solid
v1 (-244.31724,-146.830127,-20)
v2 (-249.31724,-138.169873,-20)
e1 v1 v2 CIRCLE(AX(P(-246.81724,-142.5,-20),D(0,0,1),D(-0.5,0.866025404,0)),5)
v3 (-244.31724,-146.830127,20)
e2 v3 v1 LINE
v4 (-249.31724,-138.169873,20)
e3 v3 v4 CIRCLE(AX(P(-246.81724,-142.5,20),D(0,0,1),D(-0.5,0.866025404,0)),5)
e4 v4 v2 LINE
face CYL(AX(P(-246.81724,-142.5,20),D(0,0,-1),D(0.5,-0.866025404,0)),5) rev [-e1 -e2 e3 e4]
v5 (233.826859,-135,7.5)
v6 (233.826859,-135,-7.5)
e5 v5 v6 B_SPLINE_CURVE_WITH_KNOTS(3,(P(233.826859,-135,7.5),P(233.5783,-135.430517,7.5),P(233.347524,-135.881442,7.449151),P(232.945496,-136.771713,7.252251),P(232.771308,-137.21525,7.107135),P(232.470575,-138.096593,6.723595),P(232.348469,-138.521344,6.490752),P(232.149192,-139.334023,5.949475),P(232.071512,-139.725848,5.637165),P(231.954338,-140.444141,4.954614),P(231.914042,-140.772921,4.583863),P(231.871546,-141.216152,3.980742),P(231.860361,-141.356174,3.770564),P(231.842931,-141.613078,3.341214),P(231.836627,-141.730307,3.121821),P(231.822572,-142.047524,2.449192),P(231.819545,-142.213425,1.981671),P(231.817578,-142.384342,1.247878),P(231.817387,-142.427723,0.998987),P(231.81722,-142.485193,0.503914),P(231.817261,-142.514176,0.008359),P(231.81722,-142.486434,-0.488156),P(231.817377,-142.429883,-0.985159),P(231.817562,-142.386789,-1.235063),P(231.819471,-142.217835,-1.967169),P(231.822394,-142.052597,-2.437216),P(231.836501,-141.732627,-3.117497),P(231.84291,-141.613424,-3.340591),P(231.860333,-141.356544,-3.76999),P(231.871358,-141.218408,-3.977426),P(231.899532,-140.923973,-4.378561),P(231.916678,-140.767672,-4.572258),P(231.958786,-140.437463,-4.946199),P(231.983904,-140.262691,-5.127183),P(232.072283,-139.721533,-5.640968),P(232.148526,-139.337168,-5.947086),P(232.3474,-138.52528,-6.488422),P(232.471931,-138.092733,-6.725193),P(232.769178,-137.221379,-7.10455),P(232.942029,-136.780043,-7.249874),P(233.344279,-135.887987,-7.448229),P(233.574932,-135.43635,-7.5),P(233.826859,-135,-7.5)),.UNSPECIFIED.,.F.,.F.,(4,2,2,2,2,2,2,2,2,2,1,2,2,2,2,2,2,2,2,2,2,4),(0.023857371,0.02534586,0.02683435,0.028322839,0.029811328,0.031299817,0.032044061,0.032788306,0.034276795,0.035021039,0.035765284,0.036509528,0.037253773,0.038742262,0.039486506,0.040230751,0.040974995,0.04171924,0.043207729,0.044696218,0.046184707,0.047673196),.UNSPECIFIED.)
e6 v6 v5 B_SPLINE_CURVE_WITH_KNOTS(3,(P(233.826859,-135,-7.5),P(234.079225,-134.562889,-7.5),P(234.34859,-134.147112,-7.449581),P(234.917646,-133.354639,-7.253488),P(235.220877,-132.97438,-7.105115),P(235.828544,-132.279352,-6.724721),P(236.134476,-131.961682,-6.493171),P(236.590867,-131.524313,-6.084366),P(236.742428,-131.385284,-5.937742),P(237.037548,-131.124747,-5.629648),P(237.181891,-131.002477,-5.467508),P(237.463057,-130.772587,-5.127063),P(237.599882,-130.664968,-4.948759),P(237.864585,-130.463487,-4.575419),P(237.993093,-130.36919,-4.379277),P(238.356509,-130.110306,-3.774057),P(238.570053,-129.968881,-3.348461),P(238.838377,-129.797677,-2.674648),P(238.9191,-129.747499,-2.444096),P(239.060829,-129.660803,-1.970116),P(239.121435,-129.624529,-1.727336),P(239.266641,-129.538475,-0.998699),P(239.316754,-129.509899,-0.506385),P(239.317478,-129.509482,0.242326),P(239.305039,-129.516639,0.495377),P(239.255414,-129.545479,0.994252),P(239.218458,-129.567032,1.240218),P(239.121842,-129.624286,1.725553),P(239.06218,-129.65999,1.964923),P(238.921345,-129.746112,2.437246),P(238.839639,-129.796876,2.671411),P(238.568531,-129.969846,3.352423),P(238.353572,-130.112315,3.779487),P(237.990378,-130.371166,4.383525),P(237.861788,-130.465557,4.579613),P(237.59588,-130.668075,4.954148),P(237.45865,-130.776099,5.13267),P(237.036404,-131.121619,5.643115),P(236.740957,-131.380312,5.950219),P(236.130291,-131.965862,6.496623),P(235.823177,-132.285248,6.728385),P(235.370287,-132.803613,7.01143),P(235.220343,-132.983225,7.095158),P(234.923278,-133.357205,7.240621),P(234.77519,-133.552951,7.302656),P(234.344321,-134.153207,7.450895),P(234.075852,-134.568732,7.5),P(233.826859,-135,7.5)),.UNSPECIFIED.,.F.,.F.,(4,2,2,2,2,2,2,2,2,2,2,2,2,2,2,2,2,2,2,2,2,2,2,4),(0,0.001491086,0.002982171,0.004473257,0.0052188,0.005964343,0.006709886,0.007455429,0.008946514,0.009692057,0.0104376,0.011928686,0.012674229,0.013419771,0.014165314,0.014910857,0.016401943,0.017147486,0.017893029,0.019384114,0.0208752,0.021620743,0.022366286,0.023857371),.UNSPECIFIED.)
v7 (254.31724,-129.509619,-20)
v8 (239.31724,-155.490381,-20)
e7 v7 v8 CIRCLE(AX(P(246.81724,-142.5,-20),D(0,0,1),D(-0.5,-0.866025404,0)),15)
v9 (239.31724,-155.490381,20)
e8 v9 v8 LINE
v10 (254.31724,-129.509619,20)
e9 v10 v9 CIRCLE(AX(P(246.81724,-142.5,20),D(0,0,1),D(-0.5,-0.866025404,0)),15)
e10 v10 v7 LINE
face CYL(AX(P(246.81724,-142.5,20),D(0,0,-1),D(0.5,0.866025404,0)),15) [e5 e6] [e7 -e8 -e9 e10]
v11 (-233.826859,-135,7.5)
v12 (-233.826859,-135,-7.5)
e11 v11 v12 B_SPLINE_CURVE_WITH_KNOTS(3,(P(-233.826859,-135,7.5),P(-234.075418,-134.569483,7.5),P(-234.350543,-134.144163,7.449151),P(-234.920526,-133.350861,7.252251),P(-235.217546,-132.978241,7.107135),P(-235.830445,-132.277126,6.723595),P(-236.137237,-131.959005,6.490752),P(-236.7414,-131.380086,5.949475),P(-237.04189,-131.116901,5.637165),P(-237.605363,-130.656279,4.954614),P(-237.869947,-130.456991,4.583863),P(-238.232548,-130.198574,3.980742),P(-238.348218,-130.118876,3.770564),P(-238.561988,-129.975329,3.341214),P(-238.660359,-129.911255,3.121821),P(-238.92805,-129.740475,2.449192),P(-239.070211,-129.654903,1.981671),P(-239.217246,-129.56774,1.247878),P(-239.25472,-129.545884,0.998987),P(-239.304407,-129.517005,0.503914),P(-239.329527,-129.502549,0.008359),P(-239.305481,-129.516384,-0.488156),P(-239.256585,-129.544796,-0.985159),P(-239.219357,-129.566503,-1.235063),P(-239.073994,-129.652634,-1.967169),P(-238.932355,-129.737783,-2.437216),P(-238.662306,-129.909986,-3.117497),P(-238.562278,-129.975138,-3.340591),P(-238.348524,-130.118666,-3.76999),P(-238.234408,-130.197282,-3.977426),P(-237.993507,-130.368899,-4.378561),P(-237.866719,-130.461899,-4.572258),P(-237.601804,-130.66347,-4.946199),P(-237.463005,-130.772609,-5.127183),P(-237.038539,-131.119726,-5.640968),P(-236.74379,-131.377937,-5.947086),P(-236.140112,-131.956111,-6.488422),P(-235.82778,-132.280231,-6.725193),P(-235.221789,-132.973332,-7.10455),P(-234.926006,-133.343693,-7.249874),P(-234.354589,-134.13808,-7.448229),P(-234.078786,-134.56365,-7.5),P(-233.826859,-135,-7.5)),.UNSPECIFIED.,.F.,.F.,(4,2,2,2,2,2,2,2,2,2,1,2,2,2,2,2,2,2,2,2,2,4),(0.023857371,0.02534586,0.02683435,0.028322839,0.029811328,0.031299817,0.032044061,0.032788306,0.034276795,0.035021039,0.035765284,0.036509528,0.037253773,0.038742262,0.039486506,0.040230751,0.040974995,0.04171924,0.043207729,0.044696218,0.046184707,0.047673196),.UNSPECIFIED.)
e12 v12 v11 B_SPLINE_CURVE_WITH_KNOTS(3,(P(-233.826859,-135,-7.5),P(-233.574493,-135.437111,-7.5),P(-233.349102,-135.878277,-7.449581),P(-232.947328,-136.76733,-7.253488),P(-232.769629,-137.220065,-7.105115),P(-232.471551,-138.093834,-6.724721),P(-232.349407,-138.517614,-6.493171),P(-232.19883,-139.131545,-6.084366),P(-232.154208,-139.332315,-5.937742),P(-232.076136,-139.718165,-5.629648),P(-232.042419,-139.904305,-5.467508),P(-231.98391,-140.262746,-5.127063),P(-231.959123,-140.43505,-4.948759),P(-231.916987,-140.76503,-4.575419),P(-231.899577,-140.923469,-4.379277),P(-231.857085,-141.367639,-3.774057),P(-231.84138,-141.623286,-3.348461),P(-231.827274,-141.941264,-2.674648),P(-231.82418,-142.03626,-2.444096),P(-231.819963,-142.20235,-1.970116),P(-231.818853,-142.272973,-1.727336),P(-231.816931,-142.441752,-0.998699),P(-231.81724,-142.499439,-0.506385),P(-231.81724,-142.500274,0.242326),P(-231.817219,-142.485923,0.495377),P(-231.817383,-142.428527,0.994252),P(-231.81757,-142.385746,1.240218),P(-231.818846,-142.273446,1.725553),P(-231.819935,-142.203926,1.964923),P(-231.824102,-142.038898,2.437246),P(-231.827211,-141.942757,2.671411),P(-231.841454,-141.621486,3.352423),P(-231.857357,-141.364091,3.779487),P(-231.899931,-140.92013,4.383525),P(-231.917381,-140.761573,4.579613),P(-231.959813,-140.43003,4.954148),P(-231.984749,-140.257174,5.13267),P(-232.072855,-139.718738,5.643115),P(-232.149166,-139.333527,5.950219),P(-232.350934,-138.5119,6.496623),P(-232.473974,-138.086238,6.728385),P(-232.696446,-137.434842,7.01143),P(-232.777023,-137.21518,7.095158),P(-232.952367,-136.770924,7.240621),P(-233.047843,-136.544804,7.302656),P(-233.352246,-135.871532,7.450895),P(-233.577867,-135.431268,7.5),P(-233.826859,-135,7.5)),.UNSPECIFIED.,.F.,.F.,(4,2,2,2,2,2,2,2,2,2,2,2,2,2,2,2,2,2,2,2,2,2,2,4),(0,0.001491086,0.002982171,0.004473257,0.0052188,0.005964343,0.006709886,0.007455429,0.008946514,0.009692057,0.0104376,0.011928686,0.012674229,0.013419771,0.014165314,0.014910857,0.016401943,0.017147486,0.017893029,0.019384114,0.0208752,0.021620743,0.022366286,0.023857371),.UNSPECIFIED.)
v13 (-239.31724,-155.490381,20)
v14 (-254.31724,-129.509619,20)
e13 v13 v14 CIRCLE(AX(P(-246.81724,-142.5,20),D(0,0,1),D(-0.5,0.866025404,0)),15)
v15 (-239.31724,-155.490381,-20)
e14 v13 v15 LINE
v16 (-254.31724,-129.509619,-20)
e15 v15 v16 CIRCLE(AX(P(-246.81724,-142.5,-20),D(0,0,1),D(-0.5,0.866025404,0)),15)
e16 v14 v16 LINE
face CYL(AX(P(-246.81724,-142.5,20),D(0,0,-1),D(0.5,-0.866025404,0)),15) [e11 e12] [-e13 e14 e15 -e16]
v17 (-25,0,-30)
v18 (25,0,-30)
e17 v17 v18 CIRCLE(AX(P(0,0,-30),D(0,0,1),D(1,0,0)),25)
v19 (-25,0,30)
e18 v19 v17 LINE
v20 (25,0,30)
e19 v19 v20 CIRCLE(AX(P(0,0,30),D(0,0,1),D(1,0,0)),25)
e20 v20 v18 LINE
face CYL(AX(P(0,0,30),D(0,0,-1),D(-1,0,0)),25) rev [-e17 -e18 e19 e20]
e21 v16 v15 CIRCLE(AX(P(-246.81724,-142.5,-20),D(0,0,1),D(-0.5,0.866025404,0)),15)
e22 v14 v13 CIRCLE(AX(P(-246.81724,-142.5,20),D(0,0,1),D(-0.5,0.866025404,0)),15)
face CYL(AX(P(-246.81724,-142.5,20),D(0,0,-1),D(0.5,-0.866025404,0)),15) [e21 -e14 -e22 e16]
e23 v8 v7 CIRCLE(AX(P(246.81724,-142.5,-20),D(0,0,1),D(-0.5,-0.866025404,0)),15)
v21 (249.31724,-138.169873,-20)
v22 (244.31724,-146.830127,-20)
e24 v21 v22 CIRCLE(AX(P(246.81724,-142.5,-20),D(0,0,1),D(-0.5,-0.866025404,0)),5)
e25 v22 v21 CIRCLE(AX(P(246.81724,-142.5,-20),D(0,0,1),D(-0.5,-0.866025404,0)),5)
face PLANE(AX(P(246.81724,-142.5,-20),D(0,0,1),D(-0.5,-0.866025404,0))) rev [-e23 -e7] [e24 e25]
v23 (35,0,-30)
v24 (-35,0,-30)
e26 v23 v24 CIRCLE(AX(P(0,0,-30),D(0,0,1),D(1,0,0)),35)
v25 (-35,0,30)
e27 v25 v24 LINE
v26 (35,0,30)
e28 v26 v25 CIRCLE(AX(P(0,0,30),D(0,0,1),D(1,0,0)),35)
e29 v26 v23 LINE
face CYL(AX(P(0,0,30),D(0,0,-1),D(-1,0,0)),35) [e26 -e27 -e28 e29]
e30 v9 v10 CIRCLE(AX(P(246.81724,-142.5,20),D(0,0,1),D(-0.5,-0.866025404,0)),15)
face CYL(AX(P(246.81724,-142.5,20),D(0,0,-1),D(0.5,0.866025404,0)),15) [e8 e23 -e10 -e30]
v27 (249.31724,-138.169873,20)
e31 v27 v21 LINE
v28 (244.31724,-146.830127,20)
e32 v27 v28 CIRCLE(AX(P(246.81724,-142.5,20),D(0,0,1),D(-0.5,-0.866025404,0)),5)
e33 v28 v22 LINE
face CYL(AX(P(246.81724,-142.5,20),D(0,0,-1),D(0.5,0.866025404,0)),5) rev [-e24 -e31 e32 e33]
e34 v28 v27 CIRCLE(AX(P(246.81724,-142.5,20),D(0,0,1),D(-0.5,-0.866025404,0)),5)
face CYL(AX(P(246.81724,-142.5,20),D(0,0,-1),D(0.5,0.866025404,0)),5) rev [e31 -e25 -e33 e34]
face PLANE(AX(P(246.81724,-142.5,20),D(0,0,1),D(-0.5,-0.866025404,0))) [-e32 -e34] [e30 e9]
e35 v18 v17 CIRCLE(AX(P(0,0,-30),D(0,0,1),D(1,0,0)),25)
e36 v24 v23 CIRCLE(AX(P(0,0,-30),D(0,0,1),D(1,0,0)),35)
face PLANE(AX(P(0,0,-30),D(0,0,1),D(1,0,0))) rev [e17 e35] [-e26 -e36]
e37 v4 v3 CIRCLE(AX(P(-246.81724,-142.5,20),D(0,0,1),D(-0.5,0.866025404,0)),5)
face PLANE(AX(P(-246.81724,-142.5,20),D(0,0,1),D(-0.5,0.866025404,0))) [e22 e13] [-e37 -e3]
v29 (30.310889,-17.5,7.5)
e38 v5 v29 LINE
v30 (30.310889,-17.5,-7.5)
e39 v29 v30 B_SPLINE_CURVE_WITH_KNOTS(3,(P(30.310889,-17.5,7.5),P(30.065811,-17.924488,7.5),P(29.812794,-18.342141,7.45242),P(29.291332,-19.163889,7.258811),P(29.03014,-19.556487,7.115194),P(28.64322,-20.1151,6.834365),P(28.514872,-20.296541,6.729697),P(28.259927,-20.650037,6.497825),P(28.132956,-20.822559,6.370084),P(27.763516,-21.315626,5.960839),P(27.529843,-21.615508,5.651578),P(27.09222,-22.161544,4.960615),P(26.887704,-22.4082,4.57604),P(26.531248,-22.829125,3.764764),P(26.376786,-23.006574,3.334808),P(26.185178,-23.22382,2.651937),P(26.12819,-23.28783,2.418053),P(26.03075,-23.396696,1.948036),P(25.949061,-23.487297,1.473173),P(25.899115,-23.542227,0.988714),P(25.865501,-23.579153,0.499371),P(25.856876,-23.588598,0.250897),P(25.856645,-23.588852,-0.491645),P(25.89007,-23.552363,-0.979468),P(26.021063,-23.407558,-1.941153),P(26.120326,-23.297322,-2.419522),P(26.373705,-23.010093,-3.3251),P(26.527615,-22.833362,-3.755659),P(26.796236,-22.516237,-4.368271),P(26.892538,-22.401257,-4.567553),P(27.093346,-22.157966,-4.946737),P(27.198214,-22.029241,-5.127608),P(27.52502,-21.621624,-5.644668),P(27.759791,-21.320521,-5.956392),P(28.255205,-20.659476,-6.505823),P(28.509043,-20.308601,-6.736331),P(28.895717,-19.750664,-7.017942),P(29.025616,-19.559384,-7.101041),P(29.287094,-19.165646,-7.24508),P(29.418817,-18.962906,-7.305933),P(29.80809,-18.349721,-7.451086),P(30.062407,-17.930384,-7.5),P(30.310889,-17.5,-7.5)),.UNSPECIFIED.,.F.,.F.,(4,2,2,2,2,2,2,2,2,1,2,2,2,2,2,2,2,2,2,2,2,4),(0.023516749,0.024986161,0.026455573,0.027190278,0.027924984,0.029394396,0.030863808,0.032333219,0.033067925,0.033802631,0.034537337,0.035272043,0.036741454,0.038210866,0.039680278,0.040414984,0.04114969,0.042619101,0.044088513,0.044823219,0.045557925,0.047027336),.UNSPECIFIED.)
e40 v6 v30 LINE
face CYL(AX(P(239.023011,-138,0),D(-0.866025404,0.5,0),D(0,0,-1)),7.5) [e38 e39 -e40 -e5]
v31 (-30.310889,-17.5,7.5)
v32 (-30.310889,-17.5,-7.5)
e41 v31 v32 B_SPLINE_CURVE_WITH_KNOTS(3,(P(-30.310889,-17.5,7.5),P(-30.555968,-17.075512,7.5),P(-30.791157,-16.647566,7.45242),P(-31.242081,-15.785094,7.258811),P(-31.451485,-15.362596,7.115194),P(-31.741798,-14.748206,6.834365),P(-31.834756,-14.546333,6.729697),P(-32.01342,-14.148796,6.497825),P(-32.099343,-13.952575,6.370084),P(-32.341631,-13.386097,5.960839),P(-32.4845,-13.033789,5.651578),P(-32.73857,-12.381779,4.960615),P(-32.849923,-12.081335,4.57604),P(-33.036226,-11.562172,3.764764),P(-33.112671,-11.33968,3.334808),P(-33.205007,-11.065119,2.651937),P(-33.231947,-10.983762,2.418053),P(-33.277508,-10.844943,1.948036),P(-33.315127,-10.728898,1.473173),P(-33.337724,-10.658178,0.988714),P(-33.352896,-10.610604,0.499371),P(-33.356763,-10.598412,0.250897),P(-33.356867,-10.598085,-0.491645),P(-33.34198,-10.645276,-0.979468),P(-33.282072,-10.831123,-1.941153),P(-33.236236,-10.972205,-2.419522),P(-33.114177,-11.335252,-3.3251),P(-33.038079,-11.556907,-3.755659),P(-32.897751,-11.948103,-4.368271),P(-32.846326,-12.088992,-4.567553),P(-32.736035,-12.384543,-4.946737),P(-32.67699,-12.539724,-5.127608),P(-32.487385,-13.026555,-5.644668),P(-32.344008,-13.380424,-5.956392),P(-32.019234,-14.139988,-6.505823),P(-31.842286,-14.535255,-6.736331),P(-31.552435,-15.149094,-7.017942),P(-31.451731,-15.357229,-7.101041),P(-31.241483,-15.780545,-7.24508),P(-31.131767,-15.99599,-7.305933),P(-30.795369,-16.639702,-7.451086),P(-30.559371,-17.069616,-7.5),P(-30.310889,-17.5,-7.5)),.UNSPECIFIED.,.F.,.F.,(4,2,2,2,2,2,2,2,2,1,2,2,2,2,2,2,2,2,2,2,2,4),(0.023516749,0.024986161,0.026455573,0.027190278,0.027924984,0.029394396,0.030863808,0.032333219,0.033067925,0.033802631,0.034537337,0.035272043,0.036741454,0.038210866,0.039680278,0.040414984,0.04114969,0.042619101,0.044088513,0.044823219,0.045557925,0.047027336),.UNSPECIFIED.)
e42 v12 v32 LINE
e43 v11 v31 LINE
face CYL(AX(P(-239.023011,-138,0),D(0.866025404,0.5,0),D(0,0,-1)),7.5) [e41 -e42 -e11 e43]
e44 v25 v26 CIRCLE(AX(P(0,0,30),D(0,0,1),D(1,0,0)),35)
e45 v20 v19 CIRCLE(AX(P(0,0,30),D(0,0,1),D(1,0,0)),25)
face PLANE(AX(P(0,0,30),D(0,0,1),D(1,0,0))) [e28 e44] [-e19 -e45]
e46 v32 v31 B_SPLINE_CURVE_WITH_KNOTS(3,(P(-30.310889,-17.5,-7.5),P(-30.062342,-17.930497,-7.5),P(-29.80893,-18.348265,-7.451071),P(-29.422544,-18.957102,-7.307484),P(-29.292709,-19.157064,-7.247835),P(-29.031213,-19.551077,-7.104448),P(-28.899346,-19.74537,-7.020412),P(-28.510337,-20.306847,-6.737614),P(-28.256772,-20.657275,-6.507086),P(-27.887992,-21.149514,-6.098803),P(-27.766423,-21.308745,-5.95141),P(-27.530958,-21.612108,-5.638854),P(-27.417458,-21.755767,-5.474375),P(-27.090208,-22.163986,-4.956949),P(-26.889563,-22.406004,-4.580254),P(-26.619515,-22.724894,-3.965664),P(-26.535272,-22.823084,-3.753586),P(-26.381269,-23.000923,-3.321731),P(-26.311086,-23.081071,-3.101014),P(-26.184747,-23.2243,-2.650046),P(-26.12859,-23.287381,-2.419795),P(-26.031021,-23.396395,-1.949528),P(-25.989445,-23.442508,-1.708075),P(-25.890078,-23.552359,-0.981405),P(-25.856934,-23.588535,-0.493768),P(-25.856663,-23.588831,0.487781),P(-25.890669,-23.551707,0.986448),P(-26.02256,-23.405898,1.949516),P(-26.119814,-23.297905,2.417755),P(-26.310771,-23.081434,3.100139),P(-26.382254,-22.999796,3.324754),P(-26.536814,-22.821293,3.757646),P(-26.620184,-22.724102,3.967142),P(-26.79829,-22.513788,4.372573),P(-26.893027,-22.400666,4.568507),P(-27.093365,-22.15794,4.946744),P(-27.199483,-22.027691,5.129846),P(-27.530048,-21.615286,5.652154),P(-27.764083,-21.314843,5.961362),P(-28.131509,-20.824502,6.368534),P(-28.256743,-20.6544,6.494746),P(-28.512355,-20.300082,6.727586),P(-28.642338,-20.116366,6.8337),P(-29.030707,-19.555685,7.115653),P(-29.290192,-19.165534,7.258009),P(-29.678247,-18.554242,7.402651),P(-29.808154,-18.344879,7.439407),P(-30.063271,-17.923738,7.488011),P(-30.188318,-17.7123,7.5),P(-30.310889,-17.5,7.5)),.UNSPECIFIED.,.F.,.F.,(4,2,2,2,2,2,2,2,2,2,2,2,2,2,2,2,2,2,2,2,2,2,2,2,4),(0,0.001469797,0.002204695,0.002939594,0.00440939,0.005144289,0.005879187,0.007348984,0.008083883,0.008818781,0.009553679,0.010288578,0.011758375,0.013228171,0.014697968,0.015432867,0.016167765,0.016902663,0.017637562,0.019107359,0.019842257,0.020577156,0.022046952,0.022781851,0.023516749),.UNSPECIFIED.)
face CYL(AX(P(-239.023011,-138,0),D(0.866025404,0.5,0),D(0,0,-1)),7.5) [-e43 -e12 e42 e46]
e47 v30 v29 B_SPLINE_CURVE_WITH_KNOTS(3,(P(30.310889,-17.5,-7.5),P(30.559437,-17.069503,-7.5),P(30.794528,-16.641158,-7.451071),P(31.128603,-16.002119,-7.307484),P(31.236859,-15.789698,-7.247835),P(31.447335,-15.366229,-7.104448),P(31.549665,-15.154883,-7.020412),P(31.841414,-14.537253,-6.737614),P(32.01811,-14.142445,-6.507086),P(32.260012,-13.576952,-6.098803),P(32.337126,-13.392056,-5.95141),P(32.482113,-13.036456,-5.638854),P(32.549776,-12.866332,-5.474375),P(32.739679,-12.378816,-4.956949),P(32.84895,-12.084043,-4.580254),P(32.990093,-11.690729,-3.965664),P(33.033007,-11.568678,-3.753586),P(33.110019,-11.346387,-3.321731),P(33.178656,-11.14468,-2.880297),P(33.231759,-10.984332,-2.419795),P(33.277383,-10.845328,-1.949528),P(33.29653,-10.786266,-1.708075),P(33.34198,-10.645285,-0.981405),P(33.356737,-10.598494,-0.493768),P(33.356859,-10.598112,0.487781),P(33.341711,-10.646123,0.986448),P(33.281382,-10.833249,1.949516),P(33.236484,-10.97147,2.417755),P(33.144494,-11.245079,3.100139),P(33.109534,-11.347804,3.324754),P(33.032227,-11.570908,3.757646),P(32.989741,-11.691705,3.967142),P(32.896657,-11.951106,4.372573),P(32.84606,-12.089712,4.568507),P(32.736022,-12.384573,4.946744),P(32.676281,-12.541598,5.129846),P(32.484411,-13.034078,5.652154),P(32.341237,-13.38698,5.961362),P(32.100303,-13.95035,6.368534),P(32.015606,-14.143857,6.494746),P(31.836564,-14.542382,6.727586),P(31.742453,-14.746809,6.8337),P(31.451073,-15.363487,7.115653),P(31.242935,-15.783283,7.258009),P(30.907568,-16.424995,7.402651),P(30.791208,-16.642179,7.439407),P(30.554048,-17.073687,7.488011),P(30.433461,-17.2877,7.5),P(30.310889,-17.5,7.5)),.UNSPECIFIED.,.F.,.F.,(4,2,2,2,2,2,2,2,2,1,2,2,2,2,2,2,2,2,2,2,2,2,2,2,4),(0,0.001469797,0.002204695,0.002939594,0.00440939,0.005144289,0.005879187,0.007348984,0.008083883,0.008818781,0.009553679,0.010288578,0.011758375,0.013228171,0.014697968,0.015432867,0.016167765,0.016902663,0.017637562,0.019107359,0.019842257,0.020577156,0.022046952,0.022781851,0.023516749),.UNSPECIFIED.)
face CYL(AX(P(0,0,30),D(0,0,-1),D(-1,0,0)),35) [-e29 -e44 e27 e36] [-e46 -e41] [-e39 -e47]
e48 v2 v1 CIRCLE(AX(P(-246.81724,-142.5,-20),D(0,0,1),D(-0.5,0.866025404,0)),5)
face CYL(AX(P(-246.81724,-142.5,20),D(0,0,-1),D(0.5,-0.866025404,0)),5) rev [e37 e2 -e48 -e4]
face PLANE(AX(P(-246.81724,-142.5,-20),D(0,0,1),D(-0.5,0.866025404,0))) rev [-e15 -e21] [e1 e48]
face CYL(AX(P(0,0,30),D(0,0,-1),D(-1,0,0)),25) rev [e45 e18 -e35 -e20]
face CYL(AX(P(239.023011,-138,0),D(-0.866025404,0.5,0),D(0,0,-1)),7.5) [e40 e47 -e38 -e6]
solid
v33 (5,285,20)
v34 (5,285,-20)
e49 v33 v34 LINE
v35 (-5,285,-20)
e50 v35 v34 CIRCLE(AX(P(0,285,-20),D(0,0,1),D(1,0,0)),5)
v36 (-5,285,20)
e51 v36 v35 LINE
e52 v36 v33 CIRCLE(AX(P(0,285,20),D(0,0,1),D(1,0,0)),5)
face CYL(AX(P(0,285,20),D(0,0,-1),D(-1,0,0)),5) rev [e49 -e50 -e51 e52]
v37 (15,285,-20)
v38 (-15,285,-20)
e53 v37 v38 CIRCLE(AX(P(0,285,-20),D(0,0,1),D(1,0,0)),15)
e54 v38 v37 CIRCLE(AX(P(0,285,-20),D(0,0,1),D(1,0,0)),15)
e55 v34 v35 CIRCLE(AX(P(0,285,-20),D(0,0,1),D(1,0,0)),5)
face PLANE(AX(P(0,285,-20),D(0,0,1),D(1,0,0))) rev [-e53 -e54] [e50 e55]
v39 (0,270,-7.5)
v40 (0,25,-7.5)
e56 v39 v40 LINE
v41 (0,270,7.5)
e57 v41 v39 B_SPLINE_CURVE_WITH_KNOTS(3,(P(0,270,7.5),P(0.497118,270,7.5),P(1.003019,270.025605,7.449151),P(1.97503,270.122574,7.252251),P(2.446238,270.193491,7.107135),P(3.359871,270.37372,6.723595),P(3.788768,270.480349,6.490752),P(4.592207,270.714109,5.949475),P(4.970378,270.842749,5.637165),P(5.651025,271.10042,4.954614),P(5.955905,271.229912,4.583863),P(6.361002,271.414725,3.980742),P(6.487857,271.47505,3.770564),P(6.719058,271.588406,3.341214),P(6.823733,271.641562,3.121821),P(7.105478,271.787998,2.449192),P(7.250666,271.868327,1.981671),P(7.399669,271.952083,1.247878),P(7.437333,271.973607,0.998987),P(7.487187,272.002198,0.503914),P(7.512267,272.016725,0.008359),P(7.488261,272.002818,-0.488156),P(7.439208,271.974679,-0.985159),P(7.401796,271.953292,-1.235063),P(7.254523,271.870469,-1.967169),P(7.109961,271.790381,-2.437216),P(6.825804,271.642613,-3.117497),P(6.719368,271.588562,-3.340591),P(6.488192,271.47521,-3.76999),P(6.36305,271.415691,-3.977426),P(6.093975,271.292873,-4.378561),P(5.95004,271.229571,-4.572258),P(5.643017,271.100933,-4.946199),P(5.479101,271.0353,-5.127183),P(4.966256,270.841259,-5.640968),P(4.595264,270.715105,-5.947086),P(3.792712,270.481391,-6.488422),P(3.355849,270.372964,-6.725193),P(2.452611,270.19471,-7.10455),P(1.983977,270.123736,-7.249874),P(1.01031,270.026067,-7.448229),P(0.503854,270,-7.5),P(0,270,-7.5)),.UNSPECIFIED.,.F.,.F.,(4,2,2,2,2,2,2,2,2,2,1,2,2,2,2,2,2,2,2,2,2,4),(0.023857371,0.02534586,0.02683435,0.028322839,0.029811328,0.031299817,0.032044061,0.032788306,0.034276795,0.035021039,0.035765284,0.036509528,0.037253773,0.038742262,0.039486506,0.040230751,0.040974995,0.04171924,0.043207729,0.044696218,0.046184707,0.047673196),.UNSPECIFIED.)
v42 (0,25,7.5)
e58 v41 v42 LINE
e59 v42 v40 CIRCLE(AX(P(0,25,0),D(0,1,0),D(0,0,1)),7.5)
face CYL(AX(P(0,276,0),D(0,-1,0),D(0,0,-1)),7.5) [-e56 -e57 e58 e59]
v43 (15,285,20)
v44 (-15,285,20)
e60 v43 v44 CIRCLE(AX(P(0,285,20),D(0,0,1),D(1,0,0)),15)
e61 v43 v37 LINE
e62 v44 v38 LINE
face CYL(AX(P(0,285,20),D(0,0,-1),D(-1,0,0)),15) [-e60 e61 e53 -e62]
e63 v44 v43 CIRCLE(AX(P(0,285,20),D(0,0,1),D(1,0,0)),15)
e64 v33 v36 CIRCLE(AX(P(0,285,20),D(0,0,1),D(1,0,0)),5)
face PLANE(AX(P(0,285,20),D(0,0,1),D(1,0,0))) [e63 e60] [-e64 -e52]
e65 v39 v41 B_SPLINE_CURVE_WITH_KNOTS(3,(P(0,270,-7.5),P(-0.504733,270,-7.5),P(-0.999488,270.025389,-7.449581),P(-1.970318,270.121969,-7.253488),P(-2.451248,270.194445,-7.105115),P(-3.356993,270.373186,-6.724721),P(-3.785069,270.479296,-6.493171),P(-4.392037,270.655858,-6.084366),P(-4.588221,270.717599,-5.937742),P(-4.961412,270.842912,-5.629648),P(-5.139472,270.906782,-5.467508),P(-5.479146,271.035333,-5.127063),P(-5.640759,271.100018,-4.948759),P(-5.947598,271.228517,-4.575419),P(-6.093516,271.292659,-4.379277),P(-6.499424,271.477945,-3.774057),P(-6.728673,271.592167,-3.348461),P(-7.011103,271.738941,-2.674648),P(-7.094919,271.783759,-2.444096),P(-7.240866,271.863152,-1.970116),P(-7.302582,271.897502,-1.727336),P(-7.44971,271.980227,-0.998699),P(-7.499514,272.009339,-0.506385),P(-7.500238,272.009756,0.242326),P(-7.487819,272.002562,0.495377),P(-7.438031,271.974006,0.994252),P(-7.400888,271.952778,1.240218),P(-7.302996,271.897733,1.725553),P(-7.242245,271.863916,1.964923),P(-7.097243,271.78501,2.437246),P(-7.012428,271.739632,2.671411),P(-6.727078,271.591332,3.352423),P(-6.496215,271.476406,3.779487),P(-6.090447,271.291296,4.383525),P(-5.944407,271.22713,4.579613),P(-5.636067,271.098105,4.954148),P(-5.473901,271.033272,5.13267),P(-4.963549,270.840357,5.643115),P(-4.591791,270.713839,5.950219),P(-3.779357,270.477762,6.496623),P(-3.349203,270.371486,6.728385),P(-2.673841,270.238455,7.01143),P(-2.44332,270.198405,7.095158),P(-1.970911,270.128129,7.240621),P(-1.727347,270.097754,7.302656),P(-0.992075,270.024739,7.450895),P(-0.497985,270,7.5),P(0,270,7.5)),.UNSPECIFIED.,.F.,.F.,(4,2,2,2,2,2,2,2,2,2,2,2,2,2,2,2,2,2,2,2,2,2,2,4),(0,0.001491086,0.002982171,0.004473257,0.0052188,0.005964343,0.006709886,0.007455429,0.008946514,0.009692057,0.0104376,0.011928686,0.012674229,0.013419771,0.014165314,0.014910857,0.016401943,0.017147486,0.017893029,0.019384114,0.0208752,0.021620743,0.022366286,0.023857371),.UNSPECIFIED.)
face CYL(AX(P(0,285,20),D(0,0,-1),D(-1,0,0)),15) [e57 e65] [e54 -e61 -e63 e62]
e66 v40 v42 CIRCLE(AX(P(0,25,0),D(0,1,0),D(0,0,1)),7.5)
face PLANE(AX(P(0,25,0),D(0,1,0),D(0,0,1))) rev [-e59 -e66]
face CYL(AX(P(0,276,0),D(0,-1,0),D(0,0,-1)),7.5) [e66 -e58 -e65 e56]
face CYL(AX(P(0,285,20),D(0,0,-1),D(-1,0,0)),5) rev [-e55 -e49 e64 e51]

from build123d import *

# Parameters (mm, degrees)
SKETCH1_R           = 35
SKETCH1_R_2         = 25
BOSS_EXTRUDE1_DEPTH = 30
SKETCH3_R           = 7.5
BOSS_EXTRUDE2_DEPTH = 251
SKETCH4_R           = 15
SKETCH4_R_2         = 5
BOSS_EXTRUDE3_DEPTH = 20
CIRPATTERN3_COUNT   = 3


with BuildPart() as part:
    # Sketch1 → Boss-Extrude1 (new, symmetric)
    with BuildSketch(Plane.XY):
        Circle(SKETCH1_R)
        Circle(SKETCH1_R_2, mode=Mode.SUBTRACT)
    extrude(amount=BOSS_EXTRUDE1_DEPTH, both=True)


with BuildPart() as body_2:
    # Sketch3 → Boss-Extrude2 (new body)
    with BuildSketch(Plane(origin=(0, 25, 0), x_dir=(1, 0, 0), z_dir=(0, 1, 0))):
        with Locations(Location((0, 0, 0), (0, 0, 270))):
            Circle(SKETCH3_R)
    boss_extrude2 = extrude(amount=BOSS_EXTRUDE2_DEPTH)

    # Sketch4 → Boss-Extrude3 (add, symmetric)
    with BuildSketch(Plane.XY):
        with Locations((0, 285)):
            Circle(SKETCH4_R)
        with Locations((0, 285)):
            Circle(SKETCH4_R_2, mode=Mode.SUBTRACT)
    boss_extrude3 = extrude(amount=BOSS_EXTRUDE3_DEPTH, both=True)


with BuildPart() as part_1:
    add(part.part)

    # CirPattern3: Boss-Extrude2, Boss-Extrude3 ×3 about axis
    cirpattern3_axis = Axis((0, 0, 0), (0, 0, 1))
    add([boss_extrude2.rotate(cirpattern3_axis, i * 360 / CIRPATTERN3_COUNT) for i in range(1, CIRPATTERN3_COUNT)])
    add([boss_extrude3.rotate(cirpattern3_axis, i * 360 / CIRPATTERN3_COUNT) for i in range(1, CIRPATTERN3_COUNT)])


solid = Compound([body_2.part, part_1.part])
